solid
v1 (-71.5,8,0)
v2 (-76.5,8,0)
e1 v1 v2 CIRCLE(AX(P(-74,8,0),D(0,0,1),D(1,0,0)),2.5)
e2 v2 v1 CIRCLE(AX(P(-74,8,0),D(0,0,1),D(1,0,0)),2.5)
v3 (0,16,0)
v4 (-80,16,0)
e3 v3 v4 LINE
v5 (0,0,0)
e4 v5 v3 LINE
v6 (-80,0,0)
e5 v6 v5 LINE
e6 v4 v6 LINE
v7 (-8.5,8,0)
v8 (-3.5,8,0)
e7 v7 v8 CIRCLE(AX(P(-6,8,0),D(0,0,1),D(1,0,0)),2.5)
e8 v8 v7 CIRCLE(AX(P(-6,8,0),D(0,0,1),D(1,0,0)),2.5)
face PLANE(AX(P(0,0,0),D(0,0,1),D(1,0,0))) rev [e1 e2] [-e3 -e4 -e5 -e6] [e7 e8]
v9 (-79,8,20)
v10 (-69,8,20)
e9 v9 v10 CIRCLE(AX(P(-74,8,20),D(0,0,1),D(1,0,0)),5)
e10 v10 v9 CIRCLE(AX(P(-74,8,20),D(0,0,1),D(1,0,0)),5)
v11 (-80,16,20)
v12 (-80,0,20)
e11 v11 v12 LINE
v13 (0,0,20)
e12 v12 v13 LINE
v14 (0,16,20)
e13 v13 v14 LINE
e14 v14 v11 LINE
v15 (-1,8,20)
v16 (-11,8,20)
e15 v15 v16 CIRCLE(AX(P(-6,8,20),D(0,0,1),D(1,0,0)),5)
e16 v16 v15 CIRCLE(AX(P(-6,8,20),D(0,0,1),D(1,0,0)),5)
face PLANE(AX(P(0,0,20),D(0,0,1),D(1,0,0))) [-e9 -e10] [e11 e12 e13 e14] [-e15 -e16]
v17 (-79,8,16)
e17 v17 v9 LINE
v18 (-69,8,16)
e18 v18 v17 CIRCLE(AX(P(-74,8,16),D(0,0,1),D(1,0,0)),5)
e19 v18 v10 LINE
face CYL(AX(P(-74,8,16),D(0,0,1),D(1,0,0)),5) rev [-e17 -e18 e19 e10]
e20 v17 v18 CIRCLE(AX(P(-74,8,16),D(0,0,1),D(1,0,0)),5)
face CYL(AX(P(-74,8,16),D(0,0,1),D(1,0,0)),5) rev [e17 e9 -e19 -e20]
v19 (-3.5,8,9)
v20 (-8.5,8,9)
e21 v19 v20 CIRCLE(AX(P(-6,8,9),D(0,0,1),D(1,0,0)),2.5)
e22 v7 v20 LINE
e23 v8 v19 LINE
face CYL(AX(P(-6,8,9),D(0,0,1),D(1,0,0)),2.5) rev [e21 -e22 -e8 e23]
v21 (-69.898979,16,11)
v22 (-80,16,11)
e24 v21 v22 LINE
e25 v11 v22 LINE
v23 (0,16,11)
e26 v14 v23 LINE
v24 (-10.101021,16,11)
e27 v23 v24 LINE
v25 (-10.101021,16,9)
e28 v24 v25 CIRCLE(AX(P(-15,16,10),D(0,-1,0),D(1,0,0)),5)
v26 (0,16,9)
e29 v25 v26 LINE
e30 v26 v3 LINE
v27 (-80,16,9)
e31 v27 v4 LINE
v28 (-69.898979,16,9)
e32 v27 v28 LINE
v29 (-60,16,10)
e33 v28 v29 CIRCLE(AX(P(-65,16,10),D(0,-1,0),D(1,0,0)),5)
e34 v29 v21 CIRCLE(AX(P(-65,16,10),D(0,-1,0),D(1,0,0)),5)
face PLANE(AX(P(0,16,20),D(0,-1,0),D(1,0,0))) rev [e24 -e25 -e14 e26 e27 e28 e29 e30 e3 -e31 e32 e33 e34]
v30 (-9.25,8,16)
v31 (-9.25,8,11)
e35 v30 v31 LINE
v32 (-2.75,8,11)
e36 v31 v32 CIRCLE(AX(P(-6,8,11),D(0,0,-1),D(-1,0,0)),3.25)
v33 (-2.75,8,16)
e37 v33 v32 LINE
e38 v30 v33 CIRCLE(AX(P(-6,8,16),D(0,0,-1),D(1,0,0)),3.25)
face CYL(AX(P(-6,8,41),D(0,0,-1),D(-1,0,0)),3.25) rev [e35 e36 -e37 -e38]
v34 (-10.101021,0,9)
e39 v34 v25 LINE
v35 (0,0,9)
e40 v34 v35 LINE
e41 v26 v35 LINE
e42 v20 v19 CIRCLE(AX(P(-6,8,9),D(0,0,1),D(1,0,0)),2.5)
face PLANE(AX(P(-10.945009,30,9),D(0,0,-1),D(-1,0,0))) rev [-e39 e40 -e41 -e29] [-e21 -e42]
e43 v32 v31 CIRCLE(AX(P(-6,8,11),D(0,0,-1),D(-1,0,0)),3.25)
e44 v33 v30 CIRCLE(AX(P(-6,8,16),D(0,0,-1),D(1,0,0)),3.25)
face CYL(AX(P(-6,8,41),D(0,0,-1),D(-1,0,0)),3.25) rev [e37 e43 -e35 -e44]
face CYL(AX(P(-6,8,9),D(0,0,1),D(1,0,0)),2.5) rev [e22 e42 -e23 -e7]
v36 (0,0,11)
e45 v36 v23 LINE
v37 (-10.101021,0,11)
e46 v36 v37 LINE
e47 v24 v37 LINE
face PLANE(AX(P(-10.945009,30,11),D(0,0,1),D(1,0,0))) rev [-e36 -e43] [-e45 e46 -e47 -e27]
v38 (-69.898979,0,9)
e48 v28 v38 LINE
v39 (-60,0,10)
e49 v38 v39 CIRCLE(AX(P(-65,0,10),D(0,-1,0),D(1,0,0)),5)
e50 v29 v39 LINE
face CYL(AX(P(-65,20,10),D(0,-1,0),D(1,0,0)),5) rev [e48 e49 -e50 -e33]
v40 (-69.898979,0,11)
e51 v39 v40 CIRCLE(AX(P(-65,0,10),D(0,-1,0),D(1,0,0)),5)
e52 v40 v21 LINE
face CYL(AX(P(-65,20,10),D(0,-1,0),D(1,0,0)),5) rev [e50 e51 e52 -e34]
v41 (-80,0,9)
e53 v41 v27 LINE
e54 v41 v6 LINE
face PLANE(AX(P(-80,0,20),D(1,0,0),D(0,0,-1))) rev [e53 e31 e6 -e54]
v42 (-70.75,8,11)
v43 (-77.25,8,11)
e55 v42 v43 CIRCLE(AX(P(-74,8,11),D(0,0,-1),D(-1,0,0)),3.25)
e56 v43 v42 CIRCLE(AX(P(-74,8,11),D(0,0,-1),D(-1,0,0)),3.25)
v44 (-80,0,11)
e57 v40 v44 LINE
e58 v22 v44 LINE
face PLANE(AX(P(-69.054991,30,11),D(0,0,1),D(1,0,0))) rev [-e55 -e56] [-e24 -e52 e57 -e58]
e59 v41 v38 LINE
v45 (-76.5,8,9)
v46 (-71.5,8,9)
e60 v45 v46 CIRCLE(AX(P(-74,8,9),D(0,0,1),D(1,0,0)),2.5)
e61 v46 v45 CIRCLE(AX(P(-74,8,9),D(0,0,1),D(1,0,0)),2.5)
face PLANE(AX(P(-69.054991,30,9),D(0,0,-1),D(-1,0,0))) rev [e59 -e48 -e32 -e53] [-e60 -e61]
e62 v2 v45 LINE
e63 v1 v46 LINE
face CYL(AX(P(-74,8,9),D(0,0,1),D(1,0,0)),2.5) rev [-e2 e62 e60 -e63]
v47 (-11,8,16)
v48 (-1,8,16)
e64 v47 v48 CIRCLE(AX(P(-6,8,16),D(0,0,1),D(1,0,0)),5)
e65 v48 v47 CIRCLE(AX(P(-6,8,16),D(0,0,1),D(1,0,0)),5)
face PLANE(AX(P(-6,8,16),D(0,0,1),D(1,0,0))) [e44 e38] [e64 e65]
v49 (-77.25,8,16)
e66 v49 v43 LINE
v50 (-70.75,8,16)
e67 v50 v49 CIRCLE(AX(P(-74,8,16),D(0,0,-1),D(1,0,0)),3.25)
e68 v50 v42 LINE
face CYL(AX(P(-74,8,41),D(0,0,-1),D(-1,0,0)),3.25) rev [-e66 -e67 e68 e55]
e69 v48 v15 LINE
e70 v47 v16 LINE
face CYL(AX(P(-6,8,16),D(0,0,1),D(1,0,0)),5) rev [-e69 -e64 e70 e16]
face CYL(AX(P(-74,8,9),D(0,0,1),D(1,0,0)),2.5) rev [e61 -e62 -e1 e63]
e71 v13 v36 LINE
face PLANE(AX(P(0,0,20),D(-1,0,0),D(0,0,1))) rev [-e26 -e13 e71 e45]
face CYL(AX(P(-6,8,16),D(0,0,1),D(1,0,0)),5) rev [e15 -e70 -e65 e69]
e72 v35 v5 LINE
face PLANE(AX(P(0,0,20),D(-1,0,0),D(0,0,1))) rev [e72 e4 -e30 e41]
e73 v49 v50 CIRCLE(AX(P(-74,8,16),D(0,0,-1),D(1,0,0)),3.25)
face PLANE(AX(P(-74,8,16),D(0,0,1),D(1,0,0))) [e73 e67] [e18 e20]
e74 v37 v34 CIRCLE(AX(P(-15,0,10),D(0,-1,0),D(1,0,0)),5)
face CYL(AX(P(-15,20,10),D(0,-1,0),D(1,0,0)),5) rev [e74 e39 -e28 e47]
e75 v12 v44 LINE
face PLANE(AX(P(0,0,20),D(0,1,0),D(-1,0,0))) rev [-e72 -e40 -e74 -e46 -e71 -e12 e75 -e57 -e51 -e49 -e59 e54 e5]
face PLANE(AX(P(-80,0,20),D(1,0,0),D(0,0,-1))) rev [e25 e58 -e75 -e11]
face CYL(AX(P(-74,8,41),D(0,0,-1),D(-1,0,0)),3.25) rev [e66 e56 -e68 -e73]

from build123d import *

# Parameters (mm, degrees)
SKETCH1_W                  = 80
SKETCH1_H                  = 16
BOSS_EXTRUDE1_DEPTH        = 20
SKETCH2_R                  = 5
CUT_EXTRUDE1_DEPTH         = 20
SKETCH3_W                  = 12.438334811
SKETCH3_H                  = 2
CUT_EXTRUDE2_DEPTH         = 30
M6_TAPPED_HOLE1_AT_2_COUNT = 2
M6_TAPPED_HOLE1_AT_2_PITCH = 68
SKETCH7_R                  = 3.25
CUT_EXTRUDE3_DEPTH         = 30
SKETCH8_R                  = 5
CUT_EXTRUDE7_DEPTH         = 4


with BuildPart() as part:
    # Sketch1 → Boss-Extrude1 (new body)
    with BuildSketch(Plane.XY):
        with Locations((-40, 8)):
            Rectangle(SKETCH1_W, SKETCH1_H)
    extrude(amount=BOSS_EXTRUDE1_DEPTH)

    # Sketch2 → Cut-Extrude1 (cut)
    with BuildSketch(Plane.XZ):
        with Locations((-15, 10)):
            Circle(SKETCH2_R)
        with Locations((-65, 10)):
            Circle(SKETCH2_R)
    extrude(amount=-CUT_EXTRUDE1_DEPTH, mode=Mode.SUBTRACT)

    # Sketch3 → Cut-Extrude2 (cut)
    with BuildSketch(Plane.XZ):
        with Locations((-4.725841747, 10)):
            Rectangle(SKETCH3_W, SKETCH3_H)
        with Locations((-75.274158254, 10)):
            Rectangle(SKETCH3_W, SKETCH3_H)
    extrude(amount=-CUT_EXTRUDE2_DEPTH, mode=Mode.SUBTRACT)

    # Sketch4 → M6 Tapped Hole1 (revolve, cut)
    with BuildSketch(Plane(origin=(-6, 8, 9), x_dir=(0, -1, 0), z_dir=(1, 0, 0))):
        Polygon((0, 0), (0, 18.502151548), (2.5, 17), (2.5, 0), align=None)
    m6_tapped_hole1 = revolve(axis=Axis((-6, 8, 15.35), (0, 0, -1)), mode=Mode.SUBTRACT)

    # M6 Tapped Hole1 at 2: M6 Tapped Hole1 ×2
    with Locations(*[(-i * M6_TAPPED_HOLE1_AT_2_PITCH, 0, 0) for i in range(1, M6_TAPPED_HOLE1_AT_2_COUNT)]):
        add(m6_tapped_hole1, mode=Mode.SUBTRACT)

    # Sketch7 → Cut-Extrude3 (cut)
    with BuildSketch(Plane(origin=(0, 0, 11), x_dir=(-1, 0, 0), z_dir=(0, 0, -1))):
        with Locations((74, 8)):
            Circle(SKETCH7_R)
        with Locations((6, 8)):
            Circle(SKETCH7_R)
    extrude(amount=-CUT_EXTRUDE3_DEPTH, mode=Mode.SUBTRACT)

    # Sketch8 → Cut-Extrude7 (cut)
    with BuildSketch(Plane.XY.offset(20)):
        with Locations((-6, 8)):
            Circle(SKETCH8_R)
        with Locations((-74, 8)):
            Circle(SKETCH8_R)
    extrude(amount=-CUT_EXTRUDE7_DEPTH, mode=Mode.SUBTRACT)


solid = part.part
